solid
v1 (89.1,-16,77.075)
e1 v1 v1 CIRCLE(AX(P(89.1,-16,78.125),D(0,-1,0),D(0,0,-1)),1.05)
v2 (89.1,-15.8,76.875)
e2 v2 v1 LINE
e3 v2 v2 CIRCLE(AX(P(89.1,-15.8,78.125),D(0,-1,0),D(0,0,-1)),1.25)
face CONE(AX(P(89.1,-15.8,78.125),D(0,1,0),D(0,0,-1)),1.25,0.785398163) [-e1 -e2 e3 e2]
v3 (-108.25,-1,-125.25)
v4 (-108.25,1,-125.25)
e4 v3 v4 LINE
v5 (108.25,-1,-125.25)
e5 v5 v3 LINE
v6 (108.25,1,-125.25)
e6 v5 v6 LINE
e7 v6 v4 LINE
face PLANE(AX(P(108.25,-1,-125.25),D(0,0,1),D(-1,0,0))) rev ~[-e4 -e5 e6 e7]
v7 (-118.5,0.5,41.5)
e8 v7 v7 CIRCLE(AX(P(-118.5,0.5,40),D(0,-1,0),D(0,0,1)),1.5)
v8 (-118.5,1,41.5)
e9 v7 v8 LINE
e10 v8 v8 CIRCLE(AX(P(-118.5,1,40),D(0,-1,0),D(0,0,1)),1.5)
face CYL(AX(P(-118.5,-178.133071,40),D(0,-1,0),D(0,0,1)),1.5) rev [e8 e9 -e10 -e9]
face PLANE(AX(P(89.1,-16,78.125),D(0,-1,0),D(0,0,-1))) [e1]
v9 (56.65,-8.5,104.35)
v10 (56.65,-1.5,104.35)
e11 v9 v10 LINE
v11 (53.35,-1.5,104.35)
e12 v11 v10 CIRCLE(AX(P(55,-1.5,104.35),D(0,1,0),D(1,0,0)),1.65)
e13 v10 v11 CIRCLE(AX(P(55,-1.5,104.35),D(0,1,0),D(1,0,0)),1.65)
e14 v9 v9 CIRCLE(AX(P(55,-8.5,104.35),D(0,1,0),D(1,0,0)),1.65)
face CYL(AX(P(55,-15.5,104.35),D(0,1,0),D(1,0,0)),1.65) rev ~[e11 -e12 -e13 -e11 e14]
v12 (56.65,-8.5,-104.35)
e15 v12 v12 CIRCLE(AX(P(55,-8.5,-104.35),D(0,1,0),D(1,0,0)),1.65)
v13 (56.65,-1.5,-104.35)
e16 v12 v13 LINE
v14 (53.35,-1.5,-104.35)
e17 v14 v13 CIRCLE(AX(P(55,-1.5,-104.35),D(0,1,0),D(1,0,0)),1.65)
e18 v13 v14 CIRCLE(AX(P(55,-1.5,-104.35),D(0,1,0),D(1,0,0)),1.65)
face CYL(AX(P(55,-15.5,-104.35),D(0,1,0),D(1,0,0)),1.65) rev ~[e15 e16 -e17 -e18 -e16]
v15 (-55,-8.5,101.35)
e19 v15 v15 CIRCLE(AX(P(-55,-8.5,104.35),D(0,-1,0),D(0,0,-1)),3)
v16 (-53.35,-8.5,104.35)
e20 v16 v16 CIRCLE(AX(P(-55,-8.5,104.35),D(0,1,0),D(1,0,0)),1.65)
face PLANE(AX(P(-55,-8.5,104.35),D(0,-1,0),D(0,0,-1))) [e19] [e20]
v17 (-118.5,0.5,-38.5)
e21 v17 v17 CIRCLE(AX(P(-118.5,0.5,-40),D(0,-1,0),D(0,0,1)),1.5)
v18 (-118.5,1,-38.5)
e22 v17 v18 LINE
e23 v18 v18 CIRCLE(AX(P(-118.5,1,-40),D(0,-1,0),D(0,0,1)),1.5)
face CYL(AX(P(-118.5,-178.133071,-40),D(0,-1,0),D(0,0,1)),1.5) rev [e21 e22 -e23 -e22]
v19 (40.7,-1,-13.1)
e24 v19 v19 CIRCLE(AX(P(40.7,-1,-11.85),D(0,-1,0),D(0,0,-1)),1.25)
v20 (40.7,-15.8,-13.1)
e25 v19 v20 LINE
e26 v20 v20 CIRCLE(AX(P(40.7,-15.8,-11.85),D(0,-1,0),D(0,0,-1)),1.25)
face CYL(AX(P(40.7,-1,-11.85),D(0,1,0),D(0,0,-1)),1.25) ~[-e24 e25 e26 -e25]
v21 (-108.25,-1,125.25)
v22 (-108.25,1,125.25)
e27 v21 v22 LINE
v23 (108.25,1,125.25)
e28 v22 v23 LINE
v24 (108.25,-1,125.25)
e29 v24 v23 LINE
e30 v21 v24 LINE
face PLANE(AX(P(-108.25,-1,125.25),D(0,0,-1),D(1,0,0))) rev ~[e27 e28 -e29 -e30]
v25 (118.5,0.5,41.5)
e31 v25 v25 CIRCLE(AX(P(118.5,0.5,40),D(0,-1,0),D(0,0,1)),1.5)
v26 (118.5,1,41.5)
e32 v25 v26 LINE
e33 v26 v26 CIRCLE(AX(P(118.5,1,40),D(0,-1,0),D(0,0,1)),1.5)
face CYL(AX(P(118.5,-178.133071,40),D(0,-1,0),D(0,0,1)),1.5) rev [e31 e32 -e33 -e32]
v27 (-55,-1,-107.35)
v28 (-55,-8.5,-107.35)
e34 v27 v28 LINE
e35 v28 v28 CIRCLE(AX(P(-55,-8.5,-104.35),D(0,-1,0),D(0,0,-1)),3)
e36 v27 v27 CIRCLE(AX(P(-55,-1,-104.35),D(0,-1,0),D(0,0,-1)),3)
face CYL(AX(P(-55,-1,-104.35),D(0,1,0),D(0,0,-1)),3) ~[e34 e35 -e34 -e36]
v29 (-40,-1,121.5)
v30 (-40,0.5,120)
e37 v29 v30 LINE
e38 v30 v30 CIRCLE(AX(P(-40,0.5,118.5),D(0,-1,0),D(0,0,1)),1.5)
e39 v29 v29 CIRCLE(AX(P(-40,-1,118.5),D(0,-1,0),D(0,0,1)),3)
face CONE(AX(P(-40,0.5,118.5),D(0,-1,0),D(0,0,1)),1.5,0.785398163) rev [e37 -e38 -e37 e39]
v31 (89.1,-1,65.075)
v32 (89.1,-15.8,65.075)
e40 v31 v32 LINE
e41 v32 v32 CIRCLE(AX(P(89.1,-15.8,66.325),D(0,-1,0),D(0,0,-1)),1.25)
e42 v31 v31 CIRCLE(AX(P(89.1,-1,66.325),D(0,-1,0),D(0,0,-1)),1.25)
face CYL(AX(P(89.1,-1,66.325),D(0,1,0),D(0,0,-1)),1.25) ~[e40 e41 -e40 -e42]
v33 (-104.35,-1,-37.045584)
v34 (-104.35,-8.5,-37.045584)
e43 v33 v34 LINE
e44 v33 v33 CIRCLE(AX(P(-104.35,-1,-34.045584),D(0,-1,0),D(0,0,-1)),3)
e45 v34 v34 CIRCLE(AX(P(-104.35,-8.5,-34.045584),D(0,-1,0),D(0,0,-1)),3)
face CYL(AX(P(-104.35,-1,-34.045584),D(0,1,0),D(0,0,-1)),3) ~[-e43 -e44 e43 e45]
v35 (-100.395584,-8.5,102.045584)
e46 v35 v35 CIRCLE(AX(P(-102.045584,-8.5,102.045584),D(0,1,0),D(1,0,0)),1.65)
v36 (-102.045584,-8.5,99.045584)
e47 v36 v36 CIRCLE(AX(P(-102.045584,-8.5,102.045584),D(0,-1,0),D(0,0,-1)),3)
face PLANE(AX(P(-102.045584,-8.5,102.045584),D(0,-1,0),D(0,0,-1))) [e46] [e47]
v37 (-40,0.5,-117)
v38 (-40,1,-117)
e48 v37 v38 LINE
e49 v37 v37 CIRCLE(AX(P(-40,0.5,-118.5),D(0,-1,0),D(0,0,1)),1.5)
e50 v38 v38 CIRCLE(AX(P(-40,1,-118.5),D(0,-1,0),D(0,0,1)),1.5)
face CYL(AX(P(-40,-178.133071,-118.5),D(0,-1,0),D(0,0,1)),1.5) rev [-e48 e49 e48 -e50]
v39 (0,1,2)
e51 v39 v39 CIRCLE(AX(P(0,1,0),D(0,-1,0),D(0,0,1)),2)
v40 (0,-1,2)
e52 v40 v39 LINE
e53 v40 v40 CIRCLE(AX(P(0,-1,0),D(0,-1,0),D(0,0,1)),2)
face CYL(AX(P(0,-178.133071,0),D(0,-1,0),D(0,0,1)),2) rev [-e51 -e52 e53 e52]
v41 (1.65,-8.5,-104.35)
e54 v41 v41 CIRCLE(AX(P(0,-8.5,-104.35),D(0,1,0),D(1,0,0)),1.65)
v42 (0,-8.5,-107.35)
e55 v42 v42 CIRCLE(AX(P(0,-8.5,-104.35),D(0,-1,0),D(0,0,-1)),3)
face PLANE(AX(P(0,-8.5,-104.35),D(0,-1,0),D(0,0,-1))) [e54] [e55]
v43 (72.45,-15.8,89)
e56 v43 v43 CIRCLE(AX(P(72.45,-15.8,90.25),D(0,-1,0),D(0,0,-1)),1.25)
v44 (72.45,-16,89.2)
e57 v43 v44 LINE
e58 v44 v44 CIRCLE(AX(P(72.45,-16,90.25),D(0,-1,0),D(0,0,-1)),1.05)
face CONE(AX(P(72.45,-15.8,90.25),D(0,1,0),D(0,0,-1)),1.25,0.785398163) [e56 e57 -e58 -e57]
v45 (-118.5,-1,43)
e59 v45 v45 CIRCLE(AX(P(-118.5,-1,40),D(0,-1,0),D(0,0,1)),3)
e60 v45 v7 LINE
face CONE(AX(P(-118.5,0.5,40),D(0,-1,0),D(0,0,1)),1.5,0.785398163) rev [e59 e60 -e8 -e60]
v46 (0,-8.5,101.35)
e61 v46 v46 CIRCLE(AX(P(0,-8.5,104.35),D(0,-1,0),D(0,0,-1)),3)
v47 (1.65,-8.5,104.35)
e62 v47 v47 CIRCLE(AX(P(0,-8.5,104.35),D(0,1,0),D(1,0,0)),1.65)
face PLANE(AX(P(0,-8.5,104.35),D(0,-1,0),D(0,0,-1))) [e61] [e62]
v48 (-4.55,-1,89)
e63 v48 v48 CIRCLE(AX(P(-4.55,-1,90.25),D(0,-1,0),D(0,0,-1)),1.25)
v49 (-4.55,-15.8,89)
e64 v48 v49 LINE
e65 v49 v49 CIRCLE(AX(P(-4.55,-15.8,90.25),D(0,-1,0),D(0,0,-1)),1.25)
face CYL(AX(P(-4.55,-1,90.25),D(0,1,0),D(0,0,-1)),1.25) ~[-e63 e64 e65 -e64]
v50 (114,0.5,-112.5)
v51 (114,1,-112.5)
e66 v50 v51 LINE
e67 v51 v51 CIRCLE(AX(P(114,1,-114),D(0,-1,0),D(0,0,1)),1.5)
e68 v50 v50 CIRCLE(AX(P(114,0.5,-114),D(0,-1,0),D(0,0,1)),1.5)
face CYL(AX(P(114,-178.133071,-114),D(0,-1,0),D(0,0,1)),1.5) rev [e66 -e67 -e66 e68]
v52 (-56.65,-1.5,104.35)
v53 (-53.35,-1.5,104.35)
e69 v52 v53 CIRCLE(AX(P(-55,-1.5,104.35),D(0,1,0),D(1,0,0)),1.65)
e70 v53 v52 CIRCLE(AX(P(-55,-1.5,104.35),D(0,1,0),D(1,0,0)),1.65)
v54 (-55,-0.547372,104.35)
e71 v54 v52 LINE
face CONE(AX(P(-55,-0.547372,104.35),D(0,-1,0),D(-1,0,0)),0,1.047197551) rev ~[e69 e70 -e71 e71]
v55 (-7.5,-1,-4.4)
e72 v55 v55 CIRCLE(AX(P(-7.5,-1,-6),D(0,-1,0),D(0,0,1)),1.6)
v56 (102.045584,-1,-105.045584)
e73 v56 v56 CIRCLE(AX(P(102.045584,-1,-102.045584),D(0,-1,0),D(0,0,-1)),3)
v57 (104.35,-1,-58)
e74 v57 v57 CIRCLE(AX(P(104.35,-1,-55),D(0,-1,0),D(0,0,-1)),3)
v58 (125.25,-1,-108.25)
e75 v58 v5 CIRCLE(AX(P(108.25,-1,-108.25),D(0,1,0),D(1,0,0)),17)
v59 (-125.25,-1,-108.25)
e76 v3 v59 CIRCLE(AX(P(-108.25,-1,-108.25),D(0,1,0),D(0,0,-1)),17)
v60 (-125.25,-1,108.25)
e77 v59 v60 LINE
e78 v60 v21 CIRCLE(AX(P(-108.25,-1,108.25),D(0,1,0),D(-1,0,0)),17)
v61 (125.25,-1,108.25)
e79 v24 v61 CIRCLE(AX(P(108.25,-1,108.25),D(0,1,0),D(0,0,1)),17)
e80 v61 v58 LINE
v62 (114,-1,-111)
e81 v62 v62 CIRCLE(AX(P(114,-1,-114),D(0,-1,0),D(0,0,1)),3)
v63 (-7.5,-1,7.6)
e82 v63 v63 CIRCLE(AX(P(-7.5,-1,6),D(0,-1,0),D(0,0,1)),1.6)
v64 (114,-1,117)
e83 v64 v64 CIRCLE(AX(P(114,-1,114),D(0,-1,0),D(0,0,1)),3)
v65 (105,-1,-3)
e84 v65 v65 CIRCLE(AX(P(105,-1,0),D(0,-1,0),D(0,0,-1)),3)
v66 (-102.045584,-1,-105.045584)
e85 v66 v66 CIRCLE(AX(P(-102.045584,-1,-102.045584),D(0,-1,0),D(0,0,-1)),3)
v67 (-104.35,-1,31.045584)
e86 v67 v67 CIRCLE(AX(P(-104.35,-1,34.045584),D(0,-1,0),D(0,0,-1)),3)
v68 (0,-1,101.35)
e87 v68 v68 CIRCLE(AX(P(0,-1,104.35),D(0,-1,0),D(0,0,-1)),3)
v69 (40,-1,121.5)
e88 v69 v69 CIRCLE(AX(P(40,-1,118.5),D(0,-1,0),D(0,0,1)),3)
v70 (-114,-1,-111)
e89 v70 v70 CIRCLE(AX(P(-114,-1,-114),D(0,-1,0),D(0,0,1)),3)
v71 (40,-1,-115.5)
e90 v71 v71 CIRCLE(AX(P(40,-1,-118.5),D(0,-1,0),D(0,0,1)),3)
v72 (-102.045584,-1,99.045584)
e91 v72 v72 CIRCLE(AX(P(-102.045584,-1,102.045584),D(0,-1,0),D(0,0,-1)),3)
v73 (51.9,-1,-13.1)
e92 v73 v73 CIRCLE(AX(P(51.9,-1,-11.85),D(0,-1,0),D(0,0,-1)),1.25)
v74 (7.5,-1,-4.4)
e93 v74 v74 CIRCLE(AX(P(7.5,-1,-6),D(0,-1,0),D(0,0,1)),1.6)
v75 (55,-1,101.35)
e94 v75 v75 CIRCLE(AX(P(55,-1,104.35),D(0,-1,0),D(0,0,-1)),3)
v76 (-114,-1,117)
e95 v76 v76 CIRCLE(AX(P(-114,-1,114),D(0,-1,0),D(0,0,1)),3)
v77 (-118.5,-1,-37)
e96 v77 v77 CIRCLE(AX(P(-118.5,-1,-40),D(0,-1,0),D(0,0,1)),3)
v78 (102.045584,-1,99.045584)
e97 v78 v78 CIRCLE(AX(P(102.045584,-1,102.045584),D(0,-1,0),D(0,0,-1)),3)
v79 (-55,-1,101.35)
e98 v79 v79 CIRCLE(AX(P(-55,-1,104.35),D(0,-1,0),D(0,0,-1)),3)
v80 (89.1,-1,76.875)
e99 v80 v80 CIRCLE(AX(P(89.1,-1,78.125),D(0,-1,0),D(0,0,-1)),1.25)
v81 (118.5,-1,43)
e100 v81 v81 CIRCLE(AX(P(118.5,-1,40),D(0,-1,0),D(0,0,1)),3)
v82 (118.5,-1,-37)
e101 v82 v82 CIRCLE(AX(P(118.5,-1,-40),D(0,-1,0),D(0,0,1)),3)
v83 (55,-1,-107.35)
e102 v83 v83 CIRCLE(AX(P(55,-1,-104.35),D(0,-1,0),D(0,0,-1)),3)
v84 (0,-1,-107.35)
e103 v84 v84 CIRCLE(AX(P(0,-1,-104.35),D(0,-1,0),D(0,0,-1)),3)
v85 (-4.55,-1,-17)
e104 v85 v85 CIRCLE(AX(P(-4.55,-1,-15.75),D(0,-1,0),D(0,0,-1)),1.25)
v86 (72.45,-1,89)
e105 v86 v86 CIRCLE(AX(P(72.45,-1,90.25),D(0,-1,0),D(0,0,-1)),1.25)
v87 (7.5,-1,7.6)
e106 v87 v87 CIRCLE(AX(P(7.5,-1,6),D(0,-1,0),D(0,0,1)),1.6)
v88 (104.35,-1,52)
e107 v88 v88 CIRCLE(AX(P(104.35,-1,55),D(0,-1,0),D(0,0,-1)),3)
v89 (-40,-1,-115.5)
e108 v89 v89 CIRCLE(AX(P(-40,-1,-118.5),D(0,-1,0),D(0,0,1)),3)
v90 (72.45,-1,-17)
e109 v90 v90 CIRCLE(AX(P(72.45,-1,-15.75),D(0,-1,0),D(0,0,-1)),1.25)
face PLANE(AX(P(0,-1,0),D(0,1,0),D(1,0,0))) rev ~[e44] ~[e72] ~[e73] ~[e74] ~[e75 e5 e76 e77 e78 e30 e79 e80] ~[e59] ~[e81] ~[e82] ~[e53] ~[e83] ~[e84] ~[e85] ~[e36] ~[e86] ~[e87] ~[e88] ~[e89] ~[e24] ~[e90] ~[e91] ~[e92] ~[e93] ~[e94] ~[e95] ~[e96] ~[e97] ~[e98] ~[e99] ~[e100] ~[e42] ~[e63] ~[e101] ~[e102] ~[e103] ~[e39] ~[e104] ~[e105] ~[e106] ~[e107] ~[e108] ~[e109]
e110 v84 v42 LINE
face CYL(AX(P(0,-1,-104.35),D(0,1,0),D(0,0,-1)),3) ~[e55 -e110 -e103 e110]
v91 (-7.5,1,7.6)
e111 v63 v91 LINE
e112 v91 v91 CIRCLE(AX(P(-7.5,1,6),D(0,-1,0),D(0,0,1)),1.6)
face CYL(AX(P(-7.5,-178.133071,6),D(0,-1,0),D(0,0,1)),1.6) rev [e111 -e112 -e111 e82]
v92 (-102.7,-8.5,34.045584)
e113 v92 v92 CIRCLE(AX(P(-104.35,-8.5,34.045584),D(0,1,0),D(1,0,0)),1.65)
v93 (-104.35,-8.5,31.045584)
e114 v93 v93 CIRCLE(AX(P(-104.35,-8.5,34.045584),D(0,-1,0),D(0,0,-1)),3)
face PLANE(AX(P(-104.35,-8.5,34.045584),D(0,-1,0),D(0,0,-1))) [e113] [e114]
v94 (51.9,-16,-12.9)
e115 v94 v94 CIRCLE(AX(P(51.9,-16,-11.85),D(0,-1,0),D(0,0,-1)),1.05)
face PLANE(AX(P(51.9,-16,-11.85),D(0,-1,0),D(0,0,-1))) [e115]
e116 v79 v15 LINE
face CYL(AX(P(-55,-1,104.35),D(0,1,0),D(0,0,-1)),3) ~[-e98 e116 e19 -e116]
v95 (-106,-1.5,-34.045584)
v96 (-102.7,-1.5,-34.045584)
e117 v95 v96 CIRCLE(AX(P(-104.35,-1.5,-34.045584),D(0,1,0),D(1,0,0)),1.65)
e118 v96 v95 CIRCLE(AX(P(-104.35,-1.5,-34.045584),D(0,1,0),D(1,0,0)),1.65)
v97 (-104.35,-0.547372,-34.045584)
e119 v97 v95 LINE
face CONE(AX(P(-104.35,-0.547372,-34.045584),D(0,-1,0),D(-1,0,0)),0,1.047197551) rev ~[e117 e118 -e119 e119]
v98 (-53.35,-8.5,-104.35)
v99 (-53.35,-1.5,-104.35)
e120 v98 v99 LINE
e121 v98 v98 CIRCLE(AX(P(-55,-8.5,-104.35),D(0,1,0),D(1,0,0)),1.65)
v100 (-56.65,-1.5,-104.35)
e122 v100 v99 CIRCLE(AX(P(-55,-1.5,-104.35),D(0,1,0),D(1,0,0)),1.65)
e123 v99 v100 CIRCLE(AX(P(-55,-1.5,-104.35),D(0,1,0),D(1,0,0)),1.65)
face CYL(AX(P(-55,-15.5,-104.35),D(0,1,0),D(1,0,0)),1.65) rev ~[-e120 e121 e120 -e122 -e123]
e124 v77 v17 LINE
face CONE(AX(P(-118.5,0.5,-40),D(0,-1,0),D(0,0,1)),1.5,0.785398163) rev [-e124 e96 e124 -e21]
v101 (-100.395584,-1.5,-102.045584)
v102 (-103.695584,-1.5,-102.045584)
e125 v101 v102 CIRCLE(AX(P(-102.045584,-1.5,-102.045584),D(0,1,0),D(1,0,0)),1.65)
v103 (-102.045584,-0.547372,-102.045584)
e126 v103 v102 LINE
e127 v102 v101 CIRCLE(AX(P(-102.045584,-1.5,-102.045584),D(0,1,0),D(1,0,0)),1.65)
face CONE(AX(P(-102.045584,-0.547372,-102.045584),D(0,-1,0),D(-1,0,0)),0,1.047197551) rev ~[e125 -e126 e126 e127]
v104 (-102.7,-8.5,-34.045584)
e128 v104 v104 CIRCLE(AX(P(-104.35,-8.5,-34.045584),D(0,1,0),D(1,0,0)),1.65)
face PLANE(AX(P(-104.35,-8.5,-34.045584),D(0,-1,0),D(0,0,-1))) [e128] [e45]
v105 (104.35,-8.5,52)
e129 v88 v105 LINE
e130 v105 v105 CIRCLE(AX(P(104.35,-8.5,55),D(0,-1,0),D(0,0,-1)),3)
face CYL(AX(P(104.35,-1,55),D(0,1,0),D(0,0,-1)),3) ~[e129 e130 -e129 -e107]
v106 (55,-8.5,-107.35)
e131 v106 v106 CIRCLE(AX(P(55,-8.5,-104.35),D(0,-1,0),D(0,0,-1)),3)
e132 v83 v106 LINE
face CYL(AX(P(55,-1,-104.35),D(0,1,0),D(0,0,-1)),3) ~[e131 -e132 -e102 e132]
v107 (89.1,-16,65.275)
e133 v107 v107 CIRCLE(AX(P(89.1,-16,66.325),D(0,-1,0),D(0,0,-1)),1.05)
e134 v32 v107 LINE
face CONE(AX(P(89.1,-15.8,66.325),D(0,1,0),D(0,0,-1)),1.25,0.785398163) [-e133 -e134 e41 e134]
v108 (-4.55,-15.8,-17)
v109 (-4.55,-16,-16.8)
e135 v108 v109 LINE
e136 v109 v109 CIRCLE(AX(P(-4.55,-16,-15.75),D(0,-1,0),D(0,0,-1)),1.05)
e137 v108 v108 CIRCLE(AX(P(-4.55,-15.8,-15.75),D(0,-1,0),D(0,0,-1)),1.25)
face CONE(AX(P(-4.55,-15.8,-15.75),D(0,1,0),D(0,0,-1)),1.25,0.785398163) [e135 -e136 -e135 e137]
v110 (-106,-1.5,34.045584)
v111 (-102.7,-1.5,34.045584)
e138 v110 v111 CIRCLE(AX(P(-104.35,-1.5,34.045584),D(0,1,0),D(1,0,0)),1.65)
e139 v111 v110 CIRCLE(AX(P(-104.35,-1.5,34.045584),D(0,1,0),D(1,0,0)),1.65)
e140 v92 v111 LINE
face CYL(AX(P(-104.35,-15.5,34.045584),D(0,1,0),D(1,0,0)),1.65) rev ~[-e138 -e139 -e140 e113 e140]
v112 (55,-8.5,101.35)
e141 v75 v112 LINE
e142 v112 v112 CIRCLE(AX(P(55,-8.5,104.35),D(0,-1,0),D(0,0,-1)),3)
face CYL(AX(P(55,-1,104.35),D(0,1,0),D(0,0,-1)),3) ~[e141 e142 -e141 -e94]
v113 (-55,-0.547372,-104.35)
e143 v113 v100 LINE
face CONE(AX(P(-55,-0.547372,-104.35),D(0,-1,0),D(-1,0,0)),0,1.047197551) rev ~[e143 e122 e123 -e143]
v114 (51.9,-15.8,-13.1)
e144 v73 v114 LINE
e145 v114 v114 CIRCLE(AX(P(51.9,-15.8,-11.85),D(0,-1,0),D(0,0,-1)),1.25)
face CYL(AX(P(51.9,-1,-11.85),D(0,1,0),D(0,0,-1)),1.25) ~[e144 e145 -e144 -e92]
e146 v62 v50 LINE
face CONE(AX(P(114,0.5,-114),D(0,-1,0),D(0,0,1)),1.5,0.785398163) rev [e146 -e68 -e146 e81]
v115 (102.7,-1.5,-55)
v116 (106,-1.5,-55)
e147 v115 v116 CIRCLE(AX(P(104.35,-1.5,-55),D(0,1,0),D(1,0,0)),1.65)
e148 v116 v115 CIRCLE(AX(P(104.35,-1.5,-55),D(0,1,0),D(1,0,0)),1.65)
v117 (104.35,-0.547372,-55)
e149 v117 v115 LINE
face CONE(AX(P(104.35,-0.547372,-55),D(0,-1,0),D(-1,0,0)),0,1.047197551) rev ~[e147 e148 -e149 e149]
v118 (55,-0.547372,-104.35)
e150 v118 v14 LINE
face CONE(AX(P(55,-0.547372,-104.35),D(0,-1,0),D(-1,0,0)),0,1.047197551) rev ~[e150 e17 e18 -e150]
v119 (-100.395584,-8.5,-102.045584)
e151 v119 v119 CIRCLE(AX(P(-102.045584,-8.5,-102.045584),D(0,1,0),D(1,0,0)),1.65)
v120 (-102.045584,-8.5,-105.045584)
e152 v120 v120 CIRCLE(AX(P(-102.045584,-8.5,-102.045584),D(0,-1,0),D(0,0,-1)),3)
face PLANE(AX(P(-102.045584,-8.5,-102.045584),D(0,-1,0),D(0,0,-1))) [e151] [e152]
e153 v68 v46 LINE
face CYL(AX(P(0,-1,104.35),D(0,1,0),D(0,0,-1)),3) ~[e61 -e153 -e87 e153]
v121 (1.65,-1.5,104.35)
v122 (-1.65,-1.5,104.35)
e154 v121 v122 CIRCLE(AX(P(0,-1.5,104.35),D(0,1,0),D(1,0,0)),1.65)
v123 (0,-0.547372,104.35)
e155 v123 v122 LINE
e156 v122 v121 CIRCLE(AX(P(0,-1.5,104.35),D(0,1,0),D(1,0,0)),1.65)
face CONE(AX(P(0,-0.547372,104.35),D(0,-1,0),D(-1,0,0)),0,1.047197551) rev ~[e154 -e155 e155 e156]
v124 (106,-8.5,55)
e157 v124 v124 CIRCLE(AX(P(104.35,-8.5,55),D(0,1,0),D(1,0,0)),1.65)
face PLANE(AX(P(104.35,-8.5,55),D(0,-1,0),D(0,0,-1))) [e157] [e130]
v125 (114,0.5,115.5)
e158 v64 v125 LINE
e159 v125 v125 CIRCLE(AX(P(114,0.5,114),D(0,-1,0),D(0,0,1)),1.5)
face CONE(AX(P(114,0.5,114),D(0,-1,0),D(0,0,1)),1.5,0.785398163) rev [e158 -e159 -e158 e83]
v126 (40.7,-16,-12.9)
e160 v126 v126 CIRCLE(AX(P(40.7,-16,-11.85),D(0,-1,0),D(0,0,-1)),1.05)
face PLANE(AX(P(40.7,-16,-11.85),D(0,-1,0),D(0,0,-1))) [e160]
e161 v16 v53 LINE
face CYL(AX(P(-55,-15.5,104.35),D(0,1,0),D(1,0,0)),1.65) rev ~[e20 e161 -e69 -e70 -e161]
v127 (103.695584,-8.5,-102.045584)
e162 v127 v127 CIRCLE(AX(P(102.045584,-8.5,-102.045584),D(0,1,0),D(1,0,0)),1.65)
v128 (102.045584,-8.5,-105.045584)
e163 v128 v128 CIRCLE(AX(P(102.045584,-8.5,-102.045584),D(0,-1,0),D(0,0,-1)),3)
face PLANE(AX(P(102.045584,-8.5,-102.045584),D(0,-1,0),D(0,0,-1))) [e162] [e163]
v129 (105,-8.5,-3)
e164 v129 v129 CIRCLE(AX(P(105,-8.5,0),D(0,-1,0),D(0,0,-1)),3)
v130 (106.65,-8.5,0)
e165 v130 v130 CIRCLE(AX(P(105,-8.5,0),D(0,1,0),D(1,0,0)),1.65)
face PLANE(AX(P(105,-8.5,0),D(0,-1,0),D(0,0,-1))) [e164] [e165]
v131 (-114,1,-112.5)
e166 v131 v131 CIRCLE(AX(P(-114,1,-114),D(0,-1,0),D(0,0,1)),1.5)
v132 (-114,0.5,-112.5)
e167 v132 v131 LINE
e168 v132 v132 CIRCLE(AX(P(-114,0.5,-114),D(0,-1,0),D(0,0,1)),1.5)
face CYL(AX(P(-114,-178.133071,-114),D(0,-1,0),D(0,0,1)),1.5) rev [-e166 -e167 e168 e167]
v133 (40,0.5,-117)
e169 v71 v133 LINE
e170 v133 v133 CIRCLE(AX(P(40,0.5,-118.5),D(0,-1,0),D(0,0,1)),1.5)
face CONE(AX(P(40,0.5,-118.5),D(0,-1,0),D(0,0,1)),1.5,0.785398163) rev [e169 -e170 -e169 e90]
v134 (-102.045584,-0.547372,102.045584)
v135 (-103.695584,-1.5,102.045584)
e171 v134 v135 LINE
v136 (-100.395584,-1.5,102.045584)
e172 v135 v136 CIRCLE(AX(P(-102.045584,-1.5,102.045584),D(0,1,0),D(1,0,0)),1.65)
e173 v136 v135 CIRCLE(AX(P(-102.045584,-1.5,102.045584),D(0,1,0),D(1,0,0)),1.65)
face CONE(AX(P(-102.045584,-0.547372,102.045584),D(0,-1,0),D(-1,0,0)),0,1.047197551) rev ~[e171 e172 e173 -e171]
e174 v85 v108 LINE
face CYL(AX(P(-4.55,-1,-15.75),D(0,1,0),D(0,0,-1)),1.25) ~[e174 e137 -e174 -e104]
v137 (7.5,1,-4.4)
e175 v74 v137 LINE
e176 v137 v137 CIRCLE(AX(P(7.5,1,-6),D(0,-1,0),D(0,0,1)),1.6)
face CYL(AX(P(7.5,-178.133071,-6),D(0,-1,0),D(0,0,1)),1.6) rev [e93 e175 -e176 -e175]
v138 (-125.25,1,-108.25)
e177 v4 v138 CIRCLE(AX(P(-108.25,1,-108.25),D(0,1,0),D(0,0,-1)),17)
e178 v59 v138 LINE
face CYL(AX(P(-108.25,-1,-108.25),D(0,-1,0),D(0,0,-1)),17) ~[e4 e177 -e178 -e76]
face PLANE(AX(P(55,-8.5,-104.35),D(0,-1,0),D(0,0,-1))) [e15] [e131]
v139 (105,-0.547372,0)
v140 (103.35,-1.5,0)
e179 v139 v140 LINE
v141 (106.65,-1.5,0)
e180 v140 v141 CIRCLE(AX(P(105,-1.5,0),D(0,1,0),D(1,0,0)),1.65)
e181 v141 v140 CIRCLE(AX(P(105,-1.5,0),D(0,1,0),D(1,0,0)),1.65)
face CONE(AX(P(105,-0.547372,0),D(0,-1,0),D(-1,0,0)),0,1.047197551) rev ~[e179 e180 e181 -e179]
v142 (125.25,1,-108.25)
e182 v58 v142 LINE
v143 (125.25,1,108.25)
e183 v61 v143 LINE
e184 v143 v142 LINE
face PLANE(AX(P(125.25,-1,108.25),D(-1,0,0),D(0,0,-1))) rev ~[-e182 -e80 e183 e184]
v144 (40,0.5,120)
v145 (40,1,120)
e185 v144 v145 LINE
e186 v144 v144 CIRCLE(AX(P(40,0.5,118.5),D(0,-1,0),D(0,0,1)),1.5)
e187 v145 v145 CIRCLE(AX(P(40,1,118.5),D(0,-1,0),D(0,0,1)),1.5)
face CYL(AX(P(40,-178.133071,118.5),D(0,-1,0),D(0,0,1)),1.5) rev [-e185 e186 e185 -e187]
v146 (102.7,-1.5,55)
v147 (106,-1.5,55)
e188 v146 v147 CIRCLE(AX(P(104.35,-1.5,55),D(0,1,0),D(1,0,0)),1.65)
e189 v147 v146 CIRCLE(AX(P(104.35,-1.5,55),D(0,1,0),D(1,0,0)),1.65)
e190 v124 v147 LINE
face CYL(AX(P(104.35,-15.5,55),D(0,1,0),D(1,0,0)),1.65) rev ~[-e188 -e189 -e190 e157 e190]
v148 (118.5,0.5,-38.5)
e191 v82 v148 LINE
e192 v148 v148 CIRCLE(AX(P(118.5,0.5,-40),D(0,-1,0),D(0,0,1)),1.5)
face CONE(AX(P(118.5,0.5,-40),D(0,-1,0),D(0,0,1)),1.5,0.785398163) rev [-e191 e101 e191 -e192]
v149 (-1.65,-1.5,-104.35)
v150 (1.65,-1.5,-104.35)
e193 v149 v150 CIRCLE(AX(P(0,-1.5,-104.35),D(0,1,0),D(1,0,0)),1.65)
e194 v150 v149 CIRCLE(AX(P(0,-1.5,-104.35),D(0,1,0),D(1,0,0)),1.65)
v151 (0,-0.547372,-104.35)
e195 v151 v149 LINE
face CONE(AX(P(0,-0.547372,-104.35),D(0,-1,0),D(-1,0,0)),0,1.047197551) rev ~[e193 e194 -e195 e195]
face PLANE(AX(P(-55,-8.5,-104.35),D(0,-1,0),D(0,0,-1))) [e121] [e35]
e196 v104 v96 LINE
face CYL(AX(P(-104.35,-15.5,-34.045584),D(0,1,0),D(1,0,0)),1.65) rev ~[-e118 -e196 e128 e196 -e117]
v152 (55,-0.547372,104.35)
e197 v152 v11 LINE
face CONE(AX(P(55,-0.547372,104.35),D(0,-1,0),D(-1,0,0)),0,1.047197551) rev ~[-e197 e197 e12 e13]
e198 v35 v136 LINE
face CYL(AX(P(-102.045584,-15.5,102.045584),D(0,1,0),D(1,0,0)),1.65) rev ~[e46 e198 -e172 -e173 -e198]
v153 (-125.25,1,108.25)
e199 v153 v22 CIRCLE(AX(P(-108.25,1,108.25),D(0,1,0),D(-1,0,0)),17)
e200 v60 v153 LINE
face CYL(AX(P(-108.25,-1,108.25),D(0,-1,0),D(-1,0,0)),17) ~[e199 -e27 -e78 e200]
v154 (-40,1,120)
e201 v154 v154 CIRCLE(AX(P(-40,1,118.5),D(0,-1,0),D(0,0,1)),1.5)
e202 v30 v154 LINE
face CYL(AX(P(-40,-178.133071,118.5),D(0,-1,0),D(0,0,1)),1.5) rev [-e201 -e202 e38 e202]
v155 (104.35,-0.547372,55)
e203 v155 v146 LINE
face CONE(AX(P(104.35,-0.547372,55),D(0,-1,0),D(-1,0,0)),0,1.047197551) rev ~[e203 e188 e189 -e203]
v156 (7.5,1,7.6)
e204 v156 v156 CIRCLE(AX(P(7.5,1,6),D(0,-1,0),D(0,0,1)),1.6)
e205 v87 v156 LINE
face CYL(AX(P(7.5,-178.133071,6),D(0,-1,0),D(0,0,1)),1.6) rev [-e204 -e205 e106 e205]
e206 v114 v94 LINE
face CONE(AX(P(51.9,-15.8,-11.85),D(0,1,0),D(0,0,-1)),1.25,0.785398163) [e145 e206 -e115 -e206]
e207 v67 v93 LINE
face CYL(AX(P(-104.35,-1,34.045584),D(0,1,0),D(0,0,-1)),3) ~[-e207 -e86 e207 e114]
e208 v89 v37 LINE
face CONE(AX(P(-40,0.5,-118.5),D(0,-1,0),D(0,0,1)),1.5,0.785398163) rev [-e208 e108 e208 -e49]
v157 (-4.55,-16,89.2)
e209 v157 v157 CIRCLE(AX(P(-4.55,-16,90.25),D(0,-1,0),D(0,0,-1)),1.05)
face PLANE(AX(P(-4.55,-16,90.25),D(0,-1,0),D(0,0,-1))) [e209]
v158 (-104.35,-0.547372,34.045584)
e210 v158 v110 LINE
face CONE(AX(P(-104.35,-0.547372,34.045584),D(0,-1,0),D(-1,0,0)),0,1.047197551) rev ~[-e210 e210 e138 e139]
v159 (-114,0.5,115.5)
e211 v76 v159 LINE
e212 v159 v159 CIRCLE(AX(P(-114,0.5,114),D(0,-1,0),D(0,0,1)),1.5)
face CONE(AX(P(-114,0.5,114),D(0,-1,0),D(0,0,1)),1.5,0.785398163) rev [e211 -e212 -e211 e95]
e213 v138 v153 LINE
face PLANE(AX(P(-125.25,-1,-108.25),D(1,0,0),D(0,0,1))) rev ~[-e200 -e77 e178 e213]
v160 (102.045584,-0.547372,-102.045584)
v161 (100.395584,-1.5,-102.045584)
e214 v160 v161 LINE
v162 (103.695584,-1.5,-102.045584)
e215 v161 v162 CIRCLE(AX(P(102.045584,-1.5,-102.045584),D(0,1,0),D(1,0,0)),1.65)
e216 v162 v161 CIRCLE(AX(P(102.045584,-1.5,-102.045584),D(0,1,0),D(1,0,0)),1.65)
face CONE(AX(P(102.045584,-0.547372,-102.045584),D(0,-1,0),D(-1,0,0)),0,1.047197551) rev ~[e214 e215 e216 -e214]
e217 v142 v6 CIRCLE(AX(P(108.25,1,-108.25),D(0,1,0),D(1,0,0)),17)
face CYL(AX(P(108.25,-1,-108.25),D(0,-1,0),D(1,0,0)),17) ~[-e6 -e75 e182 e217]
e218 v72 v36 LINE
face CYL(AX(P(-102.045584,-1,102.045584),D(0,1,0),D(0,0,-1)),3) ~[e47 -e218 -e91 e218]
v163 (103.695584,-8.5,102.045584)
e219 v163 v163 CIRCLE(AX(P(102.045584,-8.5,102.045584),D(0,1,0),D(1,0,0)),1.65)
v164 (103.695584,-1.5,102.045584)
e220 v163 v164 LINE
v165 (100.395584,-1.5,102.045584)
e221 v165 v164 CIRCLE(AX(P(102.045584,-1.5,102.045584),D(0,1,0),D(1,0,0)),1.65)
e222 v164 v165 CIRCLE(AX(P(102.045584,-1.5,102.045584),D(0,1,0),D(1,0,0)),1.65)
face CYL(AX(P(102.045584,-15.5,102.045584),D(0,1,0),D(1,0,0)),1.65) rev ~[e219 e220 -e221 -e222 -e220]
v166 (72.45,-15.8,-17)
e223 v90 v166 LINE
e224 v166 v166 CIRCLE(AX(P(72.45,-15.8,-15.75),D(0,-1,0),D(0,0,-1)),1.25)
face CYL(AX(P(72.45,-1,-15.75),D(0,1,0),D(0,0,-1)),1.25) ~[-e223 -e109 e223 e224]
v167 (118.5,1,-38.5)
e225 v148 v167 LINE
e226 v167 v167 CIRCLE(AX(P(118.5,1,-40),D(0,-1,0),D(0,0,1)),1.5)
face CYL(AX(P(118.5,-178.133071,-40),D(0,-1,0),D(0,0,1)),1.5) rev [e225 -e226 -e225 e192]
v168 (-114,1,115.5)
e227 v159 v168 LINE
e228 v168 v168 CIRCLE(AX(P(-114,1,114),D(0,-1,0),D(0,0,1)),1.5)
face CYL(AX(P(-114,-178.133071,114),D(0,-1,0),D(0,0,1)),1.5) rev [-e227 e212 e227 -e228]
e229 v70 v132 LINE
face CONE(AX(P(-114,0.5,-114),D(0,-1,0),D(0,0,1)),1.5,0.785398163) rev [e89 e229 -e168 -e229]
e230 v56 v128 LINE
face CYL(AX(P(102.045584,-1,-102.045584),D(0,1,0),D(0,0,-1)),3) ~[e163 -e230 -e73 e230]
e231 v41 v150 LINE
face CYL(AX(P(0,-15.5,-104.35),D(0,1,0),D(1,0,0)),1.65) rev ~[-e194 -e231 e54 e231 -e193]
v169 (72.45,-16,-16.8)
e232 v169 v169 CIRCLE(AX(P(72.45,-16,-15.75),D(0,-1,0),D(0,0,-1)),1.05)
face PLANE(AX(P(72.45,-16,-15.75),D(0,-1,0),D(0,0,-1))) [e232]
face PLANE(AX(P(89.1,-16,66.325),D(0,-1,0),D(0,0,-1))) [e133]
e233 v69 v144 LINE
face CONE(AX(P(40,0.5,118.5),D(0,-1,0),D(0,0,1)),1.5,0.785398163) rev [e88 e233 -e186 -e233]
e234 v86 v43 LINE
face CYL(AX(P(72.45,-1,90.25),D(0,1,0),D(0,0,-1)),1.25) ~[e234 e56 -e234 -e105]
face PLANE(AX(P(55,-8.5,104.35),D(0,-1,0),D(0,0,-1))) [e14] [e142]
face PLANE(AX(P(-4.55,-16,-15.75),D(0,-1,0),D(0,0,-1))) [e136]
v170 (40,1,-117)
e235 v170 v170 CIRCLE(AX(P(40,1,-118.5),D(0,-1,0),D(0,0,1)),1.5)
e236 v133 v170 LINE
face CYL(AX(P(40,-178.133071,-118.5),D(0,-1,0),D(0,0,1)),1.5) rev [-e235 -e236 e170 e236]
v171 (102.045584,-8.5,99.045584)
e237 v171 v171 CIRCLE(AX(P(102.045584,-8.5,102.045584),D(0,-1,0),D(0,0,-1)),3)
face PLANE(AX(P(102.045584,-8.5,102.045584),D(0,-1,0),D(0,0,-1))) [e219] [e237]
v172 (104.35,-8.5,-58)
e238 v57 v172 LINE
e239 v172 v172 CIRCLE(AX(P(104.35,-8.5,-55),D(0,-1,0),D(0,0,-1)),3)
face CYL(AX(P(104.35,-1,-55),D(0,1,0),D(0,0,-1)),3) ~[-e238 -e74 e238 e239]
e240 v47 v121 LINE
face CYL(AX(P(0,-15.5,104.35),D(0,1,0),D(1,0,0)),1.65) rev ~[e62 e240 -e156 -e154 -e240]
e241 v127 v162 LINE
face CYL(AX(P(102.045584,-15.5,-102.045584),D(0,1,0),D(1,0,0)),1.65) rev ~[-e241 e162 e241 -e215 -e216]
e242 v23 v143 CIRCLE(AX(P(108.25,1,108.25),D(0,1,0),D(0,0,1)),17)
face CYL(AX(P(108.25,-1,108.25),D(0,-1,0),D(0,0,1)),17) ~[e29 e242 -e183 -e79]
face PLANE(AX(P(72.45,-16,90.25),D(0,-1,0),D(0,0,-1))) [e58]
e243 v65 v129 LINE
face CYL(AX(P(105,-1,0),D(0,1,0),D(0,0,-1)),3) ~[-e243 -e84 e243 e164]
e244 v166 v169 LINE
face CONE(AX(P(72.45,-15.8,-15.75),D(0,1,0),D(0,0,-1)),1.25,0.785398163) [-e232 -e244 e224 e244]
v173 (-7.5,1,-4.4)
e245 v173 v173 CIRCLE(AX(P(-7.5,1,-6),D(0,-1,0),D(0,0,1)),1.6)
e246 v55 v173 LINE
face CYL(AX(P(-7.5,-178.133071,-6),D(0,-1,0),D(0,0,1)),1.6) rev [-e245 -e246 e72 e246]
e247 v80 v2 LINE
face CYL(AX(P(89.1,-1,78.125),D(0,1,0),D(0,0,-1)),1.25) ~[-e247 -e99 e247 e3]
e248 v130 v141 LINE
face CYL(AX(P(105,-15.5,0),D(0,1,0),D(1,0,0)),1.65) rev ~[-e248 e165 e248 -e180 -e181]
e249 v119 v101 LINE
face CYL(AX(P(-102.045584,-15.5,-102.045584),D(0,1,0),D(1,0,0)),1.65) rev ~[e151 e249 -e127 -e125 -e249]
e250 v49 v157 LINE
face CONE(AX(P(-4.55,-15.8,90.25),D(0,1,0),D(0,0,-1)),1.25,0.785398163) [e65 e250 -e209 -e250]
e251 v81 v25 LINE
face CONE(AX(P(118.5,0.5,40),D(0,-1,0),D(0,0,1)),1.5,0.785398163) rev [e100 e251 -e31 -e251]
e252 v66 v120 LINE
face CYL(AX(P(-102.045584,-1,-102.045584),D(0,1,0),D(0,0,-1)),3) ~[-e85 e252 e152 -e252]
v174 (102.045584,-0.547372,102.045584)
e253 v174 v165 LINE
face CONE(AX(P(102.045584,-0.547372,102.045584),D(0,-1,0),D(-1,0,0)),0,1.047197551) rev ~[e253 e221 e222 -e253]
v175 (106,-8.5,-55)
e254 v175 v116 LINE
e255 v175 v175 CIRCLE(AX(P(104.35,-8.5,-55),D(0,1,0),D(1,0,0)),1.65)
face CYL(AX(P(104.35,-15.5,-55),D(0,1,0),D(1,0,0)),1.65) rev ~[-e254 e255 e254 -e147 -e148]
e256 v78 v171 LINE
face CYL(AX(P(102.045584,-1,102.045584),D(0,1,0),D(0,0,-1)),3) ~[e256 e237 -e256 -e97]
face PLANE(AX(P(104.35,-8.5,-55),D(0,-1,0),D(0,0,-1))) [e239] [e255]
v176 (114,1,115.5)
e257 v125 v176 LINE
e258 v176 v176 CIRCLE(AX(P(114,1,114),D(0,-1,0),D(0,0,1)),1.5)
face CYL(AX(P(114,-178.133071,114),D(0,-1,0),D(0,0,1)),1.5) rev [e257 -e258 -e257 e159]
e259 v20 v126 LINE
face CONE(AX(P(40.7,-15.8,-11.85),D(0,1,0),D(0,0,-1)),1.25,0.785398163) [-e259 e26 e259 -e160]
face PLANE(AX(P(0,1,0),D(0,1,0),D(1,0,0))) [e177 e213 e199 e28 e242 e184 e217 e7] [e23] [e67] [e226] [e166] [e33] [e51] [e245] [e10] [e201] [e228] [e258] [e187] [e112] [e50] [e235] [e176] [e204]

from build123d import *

# Parameters (mm, degrees)
EXTRUDE_1_DEPTH          = 1
EXTRUDE_1_DEPTH_BACK     = 1
CUT_EXTRUDE_1_DEPTH      = 178.133071446
CUT_EXTRUDE_1_DEPTH_BACK = 178.133071446
SKETCH_2_R               = 1.5
SKETCH_2_R_2             = 1.6
SKETCH_2_R_3             = 2
SKETCH_3_R               = 3
EXTRUDE_2_DEPTH          = 7.5
HOLE_WIZARD_M4_1_D       = 3.3
HOLE_WIZARD_M4_1_DEPTH   = 7
HOLE_WIZARD_M4_1_TIP     = 0.952627944
CHAMFER_1_SIZE           = 1.5
SKETCH_7_R               = 1.25
EXTRUDE_3_DEPTH          = 15
CHAMFER_2_SIZE           = 0.2


with BuildPart() as part:
    # 草图1 → 凸台-拉伸1 (new, two sides: drawn at the far end of the back side and taken through both)
    with BuildSketch(Plane(origin=(0, 0, 0), x_dir=(1, 0, 0), z_dir=(0, 1, 0)).offset(-EXTRUDE_1_DEPTH_BACK)):
        with BuildLine():
            Line((-108.25, -125.25), (108.25, -125.25))
            ThreePointArc((108.25, -125.25), (120.27081528, -120.27081528), (125.25, -108.25))
            Line((125.25, -108.25), (125.25, 108.25))
            ThreePointArc((125.25, 108.25), (120.27081528, 120.27081528), (108.25, 125.25))
            Line((108.25, 125.25), (-108.25, 125.25))
            ThreePointArc((-108.25, 125.25), (-120.27081528, 120.27081528), (-125.25, 108.25))
            Line((-125.25, 108.25), (-125.25, -108.25))
            ThreePointArc((-125.25, -108.25), (-120.27081528, -120.27081528), (-108.25, -125.25))
        make_face()
    extrude(amount=EXTRUDE_1_DEPTH + EXTRUDE_1_DEPTH_BACK)

    # 草图2 → 切除-拉伸1 (cut, two sides: drawn at the far end of the back side and taken through both)
    with BuildSketch(Plane(origin=(0, 0, 0), x_dir=(1, 0, 0), z_dir=(0, 1, 0)).offset(-CUT_EXTRUDE_1_DEPTH_BACK)):
        with Locations(Location((-114, -114, 0), (0, 0, 270))):
            Circle(SKETCH_2_R)
        with Locations(Location((-40, -118.5, 0), (0, 0, 270))):
            Circle(SKETCH_2_R)
        with Locations(Location((40, -118.5, 0), (0, 0, 270))):
            Circle(SKETCH_2_R)
        with Locations(Location((-114, 114, 0), (0, 0, 270))):
            Circle(SKETCH_2_R)
        with Locations(Location((-118.5, 40, 0), (0, 0, 270))):
            Circle(SKETCH_2_R)
        with Locations(Location((-118.5, -40, 0), (0, 0, 270))):
            Circle(SKETCH_2_R)
        with Locations(Location((114, 114, 0), (0, 0, 270))):
            Circle(SKETCH_2_R)
        with Locations(Location((40, 118.5, 0), (0, 0, 270))):
            Circle(SKETCH_2_R)
        with Locations(Location((-40, 118.5, 0), (0, 0, 270))):
            Circle(SKETCH_2_R)
        with Locations(Location((114, -114, 0), (0, 0, 270))):
            Circle(SKETCH_2_R)
        with Locations(Location((118.5, -40, 0), (0, 0, 270))):
            Circle(SKETCH_2_R)
        with Locations(Location((118.5, 40, 0), (0, 0, 270))):
            Circle(SKETCH_2_R)
        with Locations(Location((-7.5, -6, 0), (0, 0, 270))):
            Circle(SKETCH_2_R_2)
        with Locations(Location((7.5, -6, 0), (0, 0, 270))):
            Circle(SKETCH_2_R_2)
        with Locations(Location((7.5, 6, 0), (0, 0, 270))):
            Circle(SKETCH_2_R_2)
        with Locations(Location((-7.5, 6, 0), (0, 0, 270))):
            Circle(SKETCH_2_R_2)
        with Locations(Location((0, 0, 0), (0, 0, 270))):
            Circle(SKETCH_2_R_3)
    extrude(amount=CUT_EXTRUDE_1_DEPTH + CUT_EXTRUDE_1_DEPTH_BACK, mode=Mode.SUBTRACT)

    # 草图3 → 凸台-拉伸2 (add)
    with BuildSketch(Plane.XZ.offset(1)):
        with Locations(Location((-102.045584412, -102.045584412, 0), (0, 0, 270))):
            Circle(SKETCH_3_R)
        with Locations(Location((-55, -104.35, 0), (0, 0, 270))):
            Circle(SKETCH_3_R)
        with Locations(Location((0, -104.35, 0), (0, 0, 270))):
            Circle(SKETCH_3_R)
        with Locations(Location((55, -104.35, 0), (0, 0, 270))):
            Circle(SKETCH_3_R)
        with Locations(Location((102.045584412, -102.045584412, 0), (0, 0, 270))):
            Circle(SKETCH_3_R)
        with Locations(Location((104.35, -55, 0), (0, 0, 270))):
            Circle(SKETCH_3_R)
        with Locations(Location((105, 0, 0), (0, 0, 270))):
            Circle(SKETCH_3_R)
        with Locations(Location((104.35, 55, 0), (0, 0, 270))):
            Circle(SKETCH_3_R)
        with Locations(Location((102.045584412, 102.045584412, 0), (0, 0, 270))):
            Circle(SKETCH_3_R)
        with Locations(Location((55, 104.35, 0), (0, 0, 270))):
            Circle(SKETCH_3_R)
        with Locations(Location((0, 104.35, 0), (0, 0, 270))):
            Circle(SKETCH_3_R)
        with Locations(Location((-55, 104.35, 0), (0, 0, 270))):
            Circle(SKETCH_3_R)
        with Locations(Location((-102.045584412, 102.045584412, 0), (0, 0, 270))):
            Circle(SKETCH_3_R)
        with Locations(Location((-104.35, 34.045584412, 0), (0, 0, 270))):
            Circle(SKETCH_3_R)
        with Locations(Location((-104.35, -34.045584412, 0), (0, 0, 270))):
            Circle(SKETCH_3_R)
    extrude(amount=EXTRUDE_2_DEPTH)

    # M4 螺纹孔1
    with Locations(Plane(origin=(0, -8.5, 0), x_dir=(-1, 0, 0), z_dir=(0, -1, 0))):
        with Locations((102.045584412, -102.045584412), (55, -104.35), (0, -104.35), (-55, -104.35), (-102.045584412, -102.045584412), (-104.35, -55), (-105, 0), (-104.35, 55), (-102.045584412, 102.045584412), (-55, 104.35), (0, 104.35), (55, 104.35), (102.045584412, 102.045584412), (104.35, 34.045584412), (104.35, -34.045584412)):
            Hole(HOLE_WIZARD_M4_1_D / 2, depth=HOLE_WIZARD_M4_1_DEPTH)
            with Locations((0, 0, -(HOLE_WIZARD_M4_1_DEPTH + HOLE_WIZARD_M4_1_TIP / 2))):  # 120° drill point
                Cone(0, HOLE_WIZARD_M4_1_D / 2, HOLE_WIZARD_M4_1_TIP, mode=Mode.SUBTRACT)

    # 倒角1
    chamfer_1_edges = [part.edges().sort_by_distance(p)[0] for p in [
        (-114, -1, 112.5),
        (-40, -1, 117),
        (40, -1, 117),
        (-114, -1, -115.5),
        (-118.5, -1, -41.5),
        (-118.5, -1, 38.5),
        (114, -1, -115.5),
        (40, -1, -120),
        (-40, -1, -120),
        (114, -1, 112.5),
        (118.5, -1, 38.5),
        (118.5, -1, -41.5),
    ]]
    chamfer(chamfer_1_edges, length=CHAMFER_1_SIZE)

    # 草图7 → 凸台-拉伸3 (add)
    with BuildSketch(Plane(origin=(0, -1, 0), x_dir=(-1, 0, 0), z_dir=(0, -1, 0))):
        with Locations(Location((4.55, 15.75, 0), (0, 0, 90))):
            Circle(SKETCH_7_R)
        with Locations(Location((-72.45, 15.75, 0), (0, 0, 90))):
            Circle(SKETCH_7_R)
        with Locations(Location((-72.45, -90.25, 0), (0, 0, 90))):
            Circle(SKETCH_7_R)
        with Locations(Location((4.55, -90.25, 0), (0, 0, 90))):
            Circle(SKETCH_7_R)
        with Locations(Location((-51.9, 11.85, 0), (0, 0, 90))):
            Circle(SKETCH_7_R)
        with Locations(Location((-40.7, 11.85, 0), (0, 0, 90))):
            Circle(SKETCH_7_R)
        with Locations(Location((-89.1, -78.125, 0), (0, 0, 90))):
            Circle(SKETCH_7_R)
        with Locations(Location((-89.1, -66.325, 0), (0, 0, 90))):
            Circle(SKETCH_7_R)
    extrude(amount=EXTRUDE_3_DEPTH)

    # 倒角2
    chamfer_2_edges = [part.edges().sort_by_distance(p)[0] for p in [
        (-4.55, -16, -14.5),
        (72.45, -16, -14.5),
        (72.45, -16, 91.5),
        (-4.55, -16, 91.5),
        (51.9, -16, -10.6),
        (40.7, -16, -10.6),
        (89.1, -16, 79.375),
        (89.1, -16, 67.575),
    ]]
    chamfer(chamfer_2_edges, length=CHAMFER_2_SIZE)


solid = part.part
